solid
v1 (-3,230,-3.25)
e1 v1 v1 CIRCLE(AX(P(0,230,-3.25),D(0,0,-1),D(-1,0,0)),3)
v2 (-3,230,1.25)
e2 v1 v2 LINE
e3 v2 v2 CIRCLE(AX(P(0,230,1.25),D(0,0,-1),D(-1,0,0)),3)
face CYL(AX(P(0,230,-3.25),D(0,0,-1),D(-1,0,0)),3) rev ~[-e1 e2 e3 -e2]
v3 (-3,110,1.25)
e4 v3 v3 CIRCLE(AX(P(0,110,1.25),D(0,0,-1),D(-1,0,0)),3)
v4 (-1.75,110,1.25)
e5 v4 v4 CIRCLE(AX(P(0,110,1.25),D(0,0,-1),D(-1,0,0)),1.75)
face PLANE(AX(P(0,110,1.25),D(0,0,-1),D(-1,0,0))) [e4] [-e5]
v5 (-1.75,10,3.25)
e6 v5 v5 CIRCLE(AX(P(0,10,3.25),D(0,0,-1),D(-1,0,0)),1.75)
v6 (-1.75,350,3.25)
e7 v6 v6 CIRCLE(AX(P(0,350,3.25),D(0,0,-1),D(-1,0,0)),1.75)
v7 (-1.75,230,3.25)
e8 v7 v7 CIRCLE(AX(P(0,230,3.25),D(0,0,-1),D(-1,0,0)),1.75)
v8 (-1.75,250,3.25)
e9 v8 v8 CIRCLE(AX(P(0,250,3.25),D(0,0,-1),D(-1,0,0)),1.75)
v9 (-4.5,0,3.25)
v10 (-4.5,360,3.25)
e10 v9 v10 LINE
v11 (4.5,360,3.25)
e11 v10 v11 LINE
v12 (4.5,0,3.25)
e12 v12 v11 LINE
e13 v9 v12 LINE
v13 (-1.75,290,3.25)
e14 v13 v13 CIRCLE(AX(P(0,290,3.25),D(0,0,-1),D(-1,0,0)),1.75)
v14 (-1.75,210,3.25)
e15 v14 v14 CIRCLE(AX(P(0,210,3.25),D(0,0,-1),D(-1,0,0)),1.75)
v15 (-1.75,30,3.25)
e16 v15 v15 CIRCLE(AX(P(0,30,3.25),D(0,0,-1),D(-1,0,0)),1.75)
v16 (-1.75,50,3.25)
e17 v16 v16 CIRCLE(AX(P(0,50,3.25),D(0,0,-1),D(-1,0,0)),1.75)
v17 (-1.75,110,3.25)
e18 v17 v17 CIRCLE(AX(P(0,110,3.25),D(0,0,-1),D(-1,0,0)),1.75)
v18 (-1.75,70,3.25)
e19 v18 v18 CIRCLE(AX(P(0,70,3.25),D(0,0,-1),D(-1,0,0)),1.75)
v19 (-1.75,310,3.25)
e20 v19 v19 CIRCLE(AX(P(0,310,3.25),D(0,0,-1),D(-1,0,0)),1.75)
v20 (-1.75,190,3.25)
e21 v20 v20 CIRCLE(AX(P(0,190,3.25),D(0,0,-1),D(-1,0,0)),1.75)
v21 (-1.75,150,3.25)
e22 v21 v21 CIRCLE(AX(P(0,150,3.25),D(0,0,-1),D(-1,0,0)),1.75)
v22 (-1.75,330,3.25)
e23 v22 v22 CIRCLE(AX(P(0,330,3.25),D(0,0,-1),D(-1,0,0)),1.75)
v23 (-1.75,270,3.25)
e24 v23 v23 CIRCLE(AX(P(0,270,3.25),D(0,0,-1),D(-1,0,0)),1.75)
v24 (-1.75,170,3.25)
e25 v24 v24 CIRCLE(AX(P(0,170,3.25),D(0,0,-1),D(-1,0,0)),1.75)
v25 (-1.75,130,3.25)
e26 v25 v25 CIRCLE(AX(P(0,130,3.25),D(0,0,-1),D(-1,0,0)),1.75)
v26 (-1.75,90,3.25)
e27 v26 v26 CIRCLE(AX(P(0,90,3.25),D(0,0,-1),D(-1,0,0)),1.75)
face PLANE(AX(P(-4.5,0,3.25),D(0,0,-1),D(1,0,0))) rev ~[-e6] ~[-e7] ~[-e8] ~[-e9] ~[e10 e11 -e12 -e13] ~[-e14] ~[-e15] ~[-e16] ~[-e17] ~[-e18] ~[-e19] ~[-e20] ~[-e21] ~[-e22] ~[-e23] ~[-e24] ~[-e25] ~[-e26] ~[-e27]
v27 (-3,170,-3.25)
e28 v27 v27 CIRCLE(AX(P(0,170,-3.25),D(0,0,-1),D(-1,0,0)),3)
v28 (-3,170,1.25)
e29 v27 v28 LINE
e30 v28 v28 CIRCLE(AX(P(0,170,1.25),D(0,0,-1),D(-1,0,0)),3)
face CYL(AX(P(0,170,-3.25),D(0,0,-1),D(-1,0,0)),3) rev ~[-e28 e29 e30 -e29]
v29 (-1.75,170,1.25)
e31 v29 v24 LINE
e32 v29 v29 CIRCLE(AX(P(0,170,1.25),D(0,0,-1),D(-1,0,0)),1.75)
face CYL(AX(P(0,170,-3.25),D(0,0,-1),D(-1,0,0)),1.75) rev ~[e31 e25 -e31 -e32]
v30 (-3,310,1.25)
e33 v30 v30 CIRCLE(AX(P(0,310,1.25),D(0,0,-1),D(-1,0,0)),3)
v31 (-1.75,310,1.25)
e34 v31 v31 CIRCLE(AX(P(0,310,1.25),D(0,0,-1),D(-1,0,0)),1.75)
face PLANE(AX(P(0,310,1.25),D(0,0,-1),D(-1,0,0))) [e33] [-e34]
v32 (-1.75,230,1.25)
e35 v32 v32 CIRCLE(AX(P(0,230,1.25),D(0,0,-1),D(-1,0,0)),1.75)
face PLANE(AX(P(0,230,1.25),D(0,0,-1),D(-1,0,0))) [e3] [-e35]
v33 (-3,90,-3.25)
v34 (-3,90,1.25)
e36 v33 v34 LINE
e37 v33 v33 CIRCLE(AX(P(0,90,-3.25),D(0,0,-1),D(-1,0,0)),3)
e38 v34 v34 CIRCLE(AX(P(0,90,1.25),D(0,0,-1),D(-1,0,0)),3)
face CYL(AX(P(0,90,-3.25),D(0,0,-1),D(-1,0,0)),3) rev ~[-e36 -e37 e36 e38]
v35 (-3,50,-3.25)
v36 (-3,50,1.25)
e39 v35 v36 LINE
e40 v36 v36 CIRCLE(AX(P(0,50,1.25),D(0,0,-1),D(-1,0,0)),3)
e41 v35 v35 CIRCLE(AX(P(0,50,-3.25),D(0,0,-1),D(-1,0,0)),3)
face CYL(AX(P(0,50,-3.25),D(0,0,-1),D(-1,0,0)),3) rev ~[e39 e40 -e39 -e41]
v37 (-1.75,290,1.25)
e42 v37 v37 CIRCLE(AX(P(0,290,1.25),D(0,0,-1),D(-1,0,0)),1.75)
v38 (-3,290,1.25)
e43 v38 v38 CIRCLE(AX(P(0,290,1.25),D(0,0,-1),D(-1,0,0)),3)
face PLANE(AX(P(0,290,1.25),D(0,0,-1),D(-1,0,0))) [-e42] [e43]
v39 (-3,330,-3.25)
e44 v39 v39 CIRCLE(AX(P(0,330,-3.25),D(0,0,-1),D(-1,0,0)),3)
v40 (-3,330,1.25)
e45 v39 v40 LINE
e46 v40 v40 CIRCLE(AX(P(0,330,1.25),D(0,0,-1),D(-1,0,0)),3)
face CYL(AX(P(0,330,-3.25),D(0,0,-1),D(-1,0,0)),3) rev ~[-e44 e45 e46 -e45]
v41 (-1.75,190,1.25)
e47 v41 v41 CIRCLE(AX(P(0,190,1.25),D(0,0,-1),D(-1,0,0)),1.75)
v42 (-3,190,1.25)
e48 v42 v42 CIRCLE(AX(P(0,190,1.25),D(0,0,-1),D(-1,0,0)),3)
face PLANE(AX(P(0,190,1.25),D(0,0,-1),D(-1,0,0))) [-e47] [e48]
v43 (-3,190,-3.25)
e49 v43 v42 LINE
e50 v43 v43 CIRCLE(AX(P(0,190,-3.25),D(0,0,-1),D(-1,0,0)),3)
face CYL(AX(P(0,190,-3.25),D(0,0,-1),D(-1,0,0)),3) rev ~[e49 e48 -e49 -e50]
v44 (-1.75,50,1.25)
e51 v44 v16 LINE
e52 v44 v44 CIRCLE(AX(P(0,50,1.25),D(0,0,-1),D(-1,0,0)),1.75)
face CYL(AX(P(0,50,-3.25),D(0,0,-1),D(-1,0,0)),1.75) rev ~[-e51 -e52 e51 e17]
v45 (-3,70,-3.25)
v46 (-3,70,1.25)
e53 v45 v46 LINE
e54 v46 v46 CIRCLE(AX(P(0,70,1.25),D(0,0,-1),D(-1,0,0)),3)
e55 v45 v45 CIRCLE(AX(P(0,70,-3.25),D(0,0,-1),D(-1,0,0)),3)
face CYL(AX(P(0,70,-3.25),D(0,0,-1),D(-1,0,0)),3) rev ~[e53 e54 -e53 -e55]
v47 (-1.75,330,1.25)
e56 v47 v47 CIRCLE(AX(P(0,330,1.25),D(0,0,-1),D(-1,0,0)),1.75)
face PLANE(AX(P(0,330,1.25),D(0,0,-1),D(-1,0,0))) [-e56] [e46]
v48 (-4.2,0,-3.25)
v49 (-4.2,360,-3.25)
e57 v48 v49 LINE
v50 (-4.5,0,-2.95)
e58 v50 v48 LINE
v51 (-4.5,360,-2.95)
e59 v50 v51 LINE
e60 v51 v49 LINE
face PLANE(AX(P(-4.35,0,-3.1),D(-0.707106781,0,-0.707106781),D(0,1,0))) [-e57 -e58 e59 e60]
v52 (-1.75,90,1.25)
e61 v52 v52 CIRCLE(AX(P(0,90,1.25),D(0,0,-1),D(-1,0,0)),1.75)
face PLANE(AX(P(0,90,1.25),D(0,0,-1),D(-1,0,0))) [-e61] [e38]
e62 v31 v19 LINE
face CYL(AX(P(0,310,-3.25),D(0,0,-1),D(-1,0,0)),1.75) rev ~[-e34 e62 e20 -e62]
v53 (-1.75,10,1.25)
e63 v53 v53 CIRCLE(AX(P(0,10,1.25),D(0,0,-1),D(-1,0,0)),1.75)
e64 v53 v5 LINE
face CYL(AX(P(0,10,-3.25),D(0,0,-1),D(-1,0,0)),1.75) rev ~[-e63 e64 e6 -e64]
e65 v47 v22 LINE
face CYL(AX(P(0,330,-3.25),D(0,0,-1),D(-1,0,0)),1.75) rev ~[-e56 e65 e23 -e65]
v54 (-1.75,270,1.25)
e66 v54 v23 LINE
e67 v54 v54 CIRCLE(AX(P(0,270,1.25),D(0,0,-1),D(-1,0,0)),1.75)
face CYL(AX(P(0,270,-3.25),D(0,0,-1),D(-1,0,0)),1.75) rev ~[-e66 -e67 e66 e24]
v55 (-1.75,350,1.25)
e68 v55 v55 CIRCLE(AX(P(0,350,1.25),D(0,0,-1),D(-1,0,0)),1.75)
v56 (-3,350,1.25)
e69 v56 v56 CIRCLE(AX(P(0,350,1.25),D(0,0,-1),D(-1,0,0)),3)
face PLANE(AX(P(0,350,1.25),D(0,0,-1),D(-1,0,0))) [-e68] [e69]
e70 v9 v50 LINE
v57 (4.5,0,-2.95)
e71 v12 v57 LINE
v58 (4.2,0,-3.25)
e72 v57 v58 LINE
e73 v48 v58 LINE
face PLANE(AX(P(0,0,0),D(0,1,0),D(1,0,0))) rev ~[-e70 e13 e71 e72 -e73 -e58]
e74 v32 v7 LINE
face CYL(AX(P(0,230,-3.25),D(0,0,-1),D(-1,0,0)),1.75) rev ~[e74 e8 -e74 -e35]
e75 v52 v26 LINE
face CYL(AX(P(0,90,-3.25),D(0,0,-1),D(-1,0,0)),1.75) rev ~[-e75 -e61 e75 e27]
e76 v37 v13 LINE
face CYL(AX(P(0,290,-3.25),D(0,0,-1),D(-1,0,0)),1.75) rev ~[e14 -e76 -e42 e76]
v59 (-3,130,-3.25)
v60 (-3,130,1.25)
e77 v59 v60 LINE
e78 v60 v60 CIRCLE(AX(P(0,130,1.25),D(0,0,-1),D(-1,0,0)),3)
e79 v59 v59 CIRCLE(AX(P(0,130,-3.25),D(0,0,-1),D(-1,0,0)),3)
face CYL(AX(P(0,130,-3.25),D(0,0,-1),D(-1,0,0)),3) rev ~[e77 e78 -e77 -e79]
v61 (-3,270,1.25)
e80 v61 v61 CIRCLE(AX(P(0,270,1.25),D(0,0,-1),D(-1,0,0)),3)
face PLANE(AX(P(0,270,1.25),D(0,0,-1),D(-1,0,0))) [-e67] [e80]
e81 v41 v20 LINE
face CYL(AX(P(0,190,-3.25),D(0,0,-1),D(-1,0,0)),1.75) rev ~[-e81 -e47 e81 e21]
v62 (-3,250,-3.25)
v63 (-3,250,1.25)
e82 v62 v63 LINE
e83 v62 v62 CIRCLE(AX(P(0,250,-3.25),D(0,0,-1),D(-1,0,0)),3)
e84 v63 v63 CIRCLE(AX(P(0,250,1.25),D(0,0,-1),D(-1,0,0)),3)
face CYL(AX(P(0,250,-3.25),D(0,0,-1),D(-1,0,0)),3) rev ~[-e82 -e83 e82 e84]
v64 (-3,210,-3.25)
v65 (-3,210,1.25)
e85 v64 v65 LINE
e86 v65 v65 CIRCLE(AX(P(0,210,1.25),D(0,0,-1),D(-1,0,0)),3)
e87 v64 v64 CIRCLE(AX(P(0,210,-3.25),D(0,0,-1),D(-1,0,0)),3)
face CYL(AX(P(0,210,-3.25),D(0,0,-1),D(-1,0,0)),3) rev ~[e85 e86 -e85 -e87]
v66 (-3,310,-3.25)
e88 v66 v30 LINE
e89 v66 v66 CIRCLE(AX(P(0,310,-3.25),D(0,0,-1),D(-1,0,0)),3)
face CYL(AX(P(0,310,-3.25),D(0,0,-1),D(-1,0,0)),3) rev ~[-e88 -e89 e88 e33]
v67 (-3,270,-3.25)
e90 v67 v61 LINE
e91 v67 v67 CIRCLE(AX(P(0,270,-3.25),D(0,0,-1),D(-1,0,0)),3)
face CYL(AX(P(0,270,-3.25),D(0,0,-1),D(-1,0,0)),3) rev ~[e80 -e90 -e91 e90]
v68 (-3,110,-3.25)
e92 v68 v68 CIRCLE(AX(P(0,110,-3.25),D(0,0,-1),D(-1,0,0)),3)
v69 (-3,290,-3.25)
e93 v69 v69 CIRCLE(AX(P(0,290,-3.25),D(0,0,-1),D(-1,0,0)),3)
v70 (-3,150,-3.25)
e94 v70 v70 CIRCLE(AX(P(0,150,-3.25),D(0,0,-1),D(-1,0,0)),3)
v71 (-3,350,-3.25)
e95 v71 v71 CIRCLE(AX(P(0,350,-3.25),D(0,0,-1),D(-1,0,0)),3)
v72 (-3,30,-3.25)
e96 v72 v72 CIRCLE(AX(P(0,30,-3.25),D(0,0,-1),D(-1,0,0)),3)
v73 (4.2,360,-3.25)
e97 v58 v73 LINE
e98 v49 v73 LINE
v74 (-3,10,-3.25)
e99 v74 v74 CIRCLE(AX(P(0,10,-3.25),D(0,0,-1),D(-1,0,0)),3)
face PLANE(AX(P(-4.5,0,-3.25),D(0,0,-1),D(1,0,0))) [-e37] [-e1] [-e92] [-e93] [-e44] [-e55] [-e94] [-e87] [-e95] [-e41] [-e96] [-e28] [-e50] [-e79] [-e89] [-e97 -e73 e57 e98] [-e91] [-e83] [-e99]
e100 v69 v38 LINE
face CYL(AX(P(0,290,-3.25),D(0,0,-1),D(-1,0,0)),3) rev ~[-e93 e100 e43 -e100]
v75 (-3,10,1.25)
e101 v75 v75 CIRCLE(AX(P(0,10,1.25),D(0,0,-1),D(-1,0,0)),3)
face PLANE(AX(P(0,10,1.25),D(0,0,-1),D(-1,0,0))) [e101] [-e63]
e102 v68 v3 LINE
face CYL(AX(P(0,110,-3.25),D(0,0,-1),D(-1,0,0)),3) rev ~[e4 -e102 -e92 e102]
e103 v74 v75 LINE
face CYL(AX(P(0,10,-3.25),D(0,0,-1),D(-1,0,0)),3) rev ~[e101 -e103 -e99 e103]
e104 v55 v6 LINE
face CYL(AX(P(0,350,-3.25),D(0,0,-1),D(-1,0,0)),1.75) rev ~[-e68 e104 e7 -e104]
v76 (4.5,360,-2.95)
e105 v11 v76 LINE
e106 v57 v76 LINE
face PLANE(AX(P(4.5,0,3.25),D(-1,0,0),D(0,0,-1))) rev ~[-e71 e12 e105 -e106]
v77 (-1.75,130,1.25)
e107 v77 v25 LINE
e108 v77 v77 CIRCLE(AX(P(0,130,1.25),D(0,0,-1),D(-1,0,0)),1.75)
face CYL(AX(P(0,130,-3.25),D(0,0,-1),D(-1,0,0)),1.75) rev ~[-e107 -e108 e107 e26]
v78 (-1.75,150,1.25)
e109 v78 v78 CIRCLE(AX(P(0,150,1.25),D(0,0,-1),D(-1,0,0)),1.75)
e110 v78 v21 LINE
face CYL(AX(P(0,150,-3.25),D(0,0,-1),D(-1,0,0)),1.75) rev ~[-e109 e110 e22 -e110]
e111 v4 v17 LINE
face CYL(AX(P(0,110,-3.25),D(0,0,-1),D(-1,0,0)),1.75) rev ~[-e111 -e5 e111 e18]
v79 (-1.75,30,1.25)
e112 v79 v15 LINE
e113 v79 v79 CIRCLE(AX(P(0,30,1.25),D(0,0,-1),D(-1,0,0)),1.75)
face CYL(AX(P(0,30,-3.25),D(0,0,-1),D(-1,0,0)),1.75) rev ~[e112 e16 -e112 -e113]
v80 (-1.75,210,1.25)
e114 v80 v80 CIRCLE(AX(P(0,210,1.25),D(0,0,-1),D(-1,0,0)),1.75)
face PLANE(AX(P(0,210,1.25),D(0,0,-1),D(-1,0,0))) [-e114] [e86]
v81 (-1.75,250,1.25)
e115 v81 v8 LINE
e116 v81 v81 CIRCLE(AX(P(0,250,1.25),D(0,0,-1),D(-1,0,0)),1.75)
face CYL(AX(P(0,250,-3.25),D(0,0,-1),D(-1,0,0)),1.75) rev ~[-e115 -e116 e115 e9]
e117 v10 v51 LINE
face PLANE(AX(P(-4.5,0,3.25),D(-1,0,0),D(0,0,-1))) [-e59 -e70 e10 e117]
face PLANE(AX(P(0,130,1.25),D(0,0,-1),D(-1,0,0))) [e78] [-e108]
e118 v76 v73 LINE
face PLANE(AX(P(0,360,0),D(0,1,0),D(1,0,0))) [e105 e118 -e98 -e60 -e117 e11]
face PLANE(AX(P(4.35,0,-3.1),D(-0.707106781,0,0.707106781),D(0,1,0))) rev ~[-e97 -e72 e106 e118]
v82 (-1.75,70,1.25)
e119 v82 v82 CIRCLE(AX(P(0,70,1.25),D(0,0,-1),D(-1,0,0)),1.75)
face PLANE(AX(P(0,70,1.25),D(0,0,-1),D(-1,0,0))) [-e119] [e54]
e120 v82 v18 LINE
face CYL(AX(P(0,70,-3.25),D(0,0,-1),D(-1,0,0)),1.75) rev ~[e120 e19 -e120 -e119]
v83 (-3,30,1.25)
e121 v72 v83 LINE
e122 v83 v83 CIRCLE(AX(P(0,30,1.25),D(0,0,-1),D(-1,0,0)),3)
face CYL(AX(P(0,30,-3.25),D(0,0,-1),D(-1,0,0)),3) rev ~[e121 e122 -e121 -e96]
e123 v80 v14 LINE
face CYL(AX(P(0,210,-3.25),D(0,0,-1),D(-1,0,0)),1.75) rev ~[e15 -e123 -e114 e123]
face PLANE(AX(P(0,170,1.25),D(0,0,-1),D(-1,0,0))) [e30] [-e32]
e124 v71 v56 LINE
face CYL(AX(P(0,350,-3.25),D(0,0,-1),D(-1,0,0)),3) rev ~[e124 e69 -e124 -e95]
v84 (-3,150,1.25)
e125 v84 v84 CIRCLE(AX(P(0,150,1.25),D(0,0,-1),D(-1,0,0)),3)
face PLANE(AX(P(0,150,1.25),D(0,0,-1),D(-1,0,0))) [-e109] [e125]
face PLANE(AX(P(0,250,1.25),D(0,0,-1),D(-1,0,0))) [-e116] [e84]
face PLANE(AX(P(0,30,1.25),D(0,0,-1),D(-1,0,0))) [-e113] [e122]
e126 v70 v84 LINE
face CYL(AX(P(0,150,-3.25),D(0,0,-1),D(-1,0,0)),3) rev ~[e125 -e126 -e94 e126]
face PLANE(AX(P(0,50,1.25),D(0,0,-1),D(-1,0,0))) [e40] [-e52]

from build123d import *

# Parameters (mm, degrees)
SKETCH1_W           = 9
SKETCH1_H           = 6.5
BOSS_EXTRUDE1_DEPTH = 360
CHAMFER1_SIZE       = 0.3
SKETCH2_R           = 1.75
CUT_EXTRUDE1_DEPTH  = 37
LPATTERN1_COUNT     = 18
LPATTERN1_PITCH     = 20
SKETCH3_R           = 3
CUT_EXTRUDE2_DEPTH  = 4.5
LPATTERN2_COUNT     = 18
LPATTERN2_PITCH     = 20


with BuildPart() as part:
    # Sketch1 → Boss-Extrude1 (new body)
    with BuildSketch(Plane(origin=(0, 0, 0), x_dir=(1, 0, 0), z_dir=(0, 1, 0))):
        Rectangle(SKETCH1_W, SKETCH1_H)
    extrude(amount=BOSS_EXTRUDE1_DEPTH)

    # Chamfer1
    chamfer1_edges = [part.edges().sort_by_distance(p)[0] for p in [
        (-4.5, 180, -3.25),
        (4.5, 180, -3.25),
    ]]
    chamfer(chamfer1_edges, length=CHAMFER1_SIZE)

    # Sketch2 → Cut-Extrude1 (cut)
    with BuildSketch(Plane(origin=(0, 0, -3.25), x_dir=(-1, 0, 0), z_dir=(0, 0, -1))):
        with Locations((0, 10)):
            Circle(SKETCH2_R)
    cut_extrude1 = extrude(amount=-CUT_EXTRUDE1_DEPTH, mode=Mode.SUBTRACT)

    # LPattern1: Cut-Extrude1 ×18
    with Locations(*[(0, i * LPATTERN1_PITCH, 0) for i in range(1, LPATTERN1_COUNT)]):
        add(cut_extrude1, mode=Mode.SUBTRACT)

    # Sketch3 → Cut-Extrude2 (cut)
    with BuildSketch(Plane(origin=(0, 0, -3.25), x_dir=(-1, 0, 0), z_dir=(0, 0, -1))):
        with Locations((0, 10)):
            Circle(SKETCH3_R)
    cut_extrude2 = extrude(amount=-CUT_EXTRUDE2_DEPTH, mode=Mode.SUBTRACT)

    # LPattern2: Cut-Extrude2 ×18
    with Locations(*[(0, i * LPATTERN2_PITCH, 0) for i in range(1, LPATTERN2_COUNT)]):
        add(cut_extrude2, mode=Mode.SUBTRACT)


solid = part.part
